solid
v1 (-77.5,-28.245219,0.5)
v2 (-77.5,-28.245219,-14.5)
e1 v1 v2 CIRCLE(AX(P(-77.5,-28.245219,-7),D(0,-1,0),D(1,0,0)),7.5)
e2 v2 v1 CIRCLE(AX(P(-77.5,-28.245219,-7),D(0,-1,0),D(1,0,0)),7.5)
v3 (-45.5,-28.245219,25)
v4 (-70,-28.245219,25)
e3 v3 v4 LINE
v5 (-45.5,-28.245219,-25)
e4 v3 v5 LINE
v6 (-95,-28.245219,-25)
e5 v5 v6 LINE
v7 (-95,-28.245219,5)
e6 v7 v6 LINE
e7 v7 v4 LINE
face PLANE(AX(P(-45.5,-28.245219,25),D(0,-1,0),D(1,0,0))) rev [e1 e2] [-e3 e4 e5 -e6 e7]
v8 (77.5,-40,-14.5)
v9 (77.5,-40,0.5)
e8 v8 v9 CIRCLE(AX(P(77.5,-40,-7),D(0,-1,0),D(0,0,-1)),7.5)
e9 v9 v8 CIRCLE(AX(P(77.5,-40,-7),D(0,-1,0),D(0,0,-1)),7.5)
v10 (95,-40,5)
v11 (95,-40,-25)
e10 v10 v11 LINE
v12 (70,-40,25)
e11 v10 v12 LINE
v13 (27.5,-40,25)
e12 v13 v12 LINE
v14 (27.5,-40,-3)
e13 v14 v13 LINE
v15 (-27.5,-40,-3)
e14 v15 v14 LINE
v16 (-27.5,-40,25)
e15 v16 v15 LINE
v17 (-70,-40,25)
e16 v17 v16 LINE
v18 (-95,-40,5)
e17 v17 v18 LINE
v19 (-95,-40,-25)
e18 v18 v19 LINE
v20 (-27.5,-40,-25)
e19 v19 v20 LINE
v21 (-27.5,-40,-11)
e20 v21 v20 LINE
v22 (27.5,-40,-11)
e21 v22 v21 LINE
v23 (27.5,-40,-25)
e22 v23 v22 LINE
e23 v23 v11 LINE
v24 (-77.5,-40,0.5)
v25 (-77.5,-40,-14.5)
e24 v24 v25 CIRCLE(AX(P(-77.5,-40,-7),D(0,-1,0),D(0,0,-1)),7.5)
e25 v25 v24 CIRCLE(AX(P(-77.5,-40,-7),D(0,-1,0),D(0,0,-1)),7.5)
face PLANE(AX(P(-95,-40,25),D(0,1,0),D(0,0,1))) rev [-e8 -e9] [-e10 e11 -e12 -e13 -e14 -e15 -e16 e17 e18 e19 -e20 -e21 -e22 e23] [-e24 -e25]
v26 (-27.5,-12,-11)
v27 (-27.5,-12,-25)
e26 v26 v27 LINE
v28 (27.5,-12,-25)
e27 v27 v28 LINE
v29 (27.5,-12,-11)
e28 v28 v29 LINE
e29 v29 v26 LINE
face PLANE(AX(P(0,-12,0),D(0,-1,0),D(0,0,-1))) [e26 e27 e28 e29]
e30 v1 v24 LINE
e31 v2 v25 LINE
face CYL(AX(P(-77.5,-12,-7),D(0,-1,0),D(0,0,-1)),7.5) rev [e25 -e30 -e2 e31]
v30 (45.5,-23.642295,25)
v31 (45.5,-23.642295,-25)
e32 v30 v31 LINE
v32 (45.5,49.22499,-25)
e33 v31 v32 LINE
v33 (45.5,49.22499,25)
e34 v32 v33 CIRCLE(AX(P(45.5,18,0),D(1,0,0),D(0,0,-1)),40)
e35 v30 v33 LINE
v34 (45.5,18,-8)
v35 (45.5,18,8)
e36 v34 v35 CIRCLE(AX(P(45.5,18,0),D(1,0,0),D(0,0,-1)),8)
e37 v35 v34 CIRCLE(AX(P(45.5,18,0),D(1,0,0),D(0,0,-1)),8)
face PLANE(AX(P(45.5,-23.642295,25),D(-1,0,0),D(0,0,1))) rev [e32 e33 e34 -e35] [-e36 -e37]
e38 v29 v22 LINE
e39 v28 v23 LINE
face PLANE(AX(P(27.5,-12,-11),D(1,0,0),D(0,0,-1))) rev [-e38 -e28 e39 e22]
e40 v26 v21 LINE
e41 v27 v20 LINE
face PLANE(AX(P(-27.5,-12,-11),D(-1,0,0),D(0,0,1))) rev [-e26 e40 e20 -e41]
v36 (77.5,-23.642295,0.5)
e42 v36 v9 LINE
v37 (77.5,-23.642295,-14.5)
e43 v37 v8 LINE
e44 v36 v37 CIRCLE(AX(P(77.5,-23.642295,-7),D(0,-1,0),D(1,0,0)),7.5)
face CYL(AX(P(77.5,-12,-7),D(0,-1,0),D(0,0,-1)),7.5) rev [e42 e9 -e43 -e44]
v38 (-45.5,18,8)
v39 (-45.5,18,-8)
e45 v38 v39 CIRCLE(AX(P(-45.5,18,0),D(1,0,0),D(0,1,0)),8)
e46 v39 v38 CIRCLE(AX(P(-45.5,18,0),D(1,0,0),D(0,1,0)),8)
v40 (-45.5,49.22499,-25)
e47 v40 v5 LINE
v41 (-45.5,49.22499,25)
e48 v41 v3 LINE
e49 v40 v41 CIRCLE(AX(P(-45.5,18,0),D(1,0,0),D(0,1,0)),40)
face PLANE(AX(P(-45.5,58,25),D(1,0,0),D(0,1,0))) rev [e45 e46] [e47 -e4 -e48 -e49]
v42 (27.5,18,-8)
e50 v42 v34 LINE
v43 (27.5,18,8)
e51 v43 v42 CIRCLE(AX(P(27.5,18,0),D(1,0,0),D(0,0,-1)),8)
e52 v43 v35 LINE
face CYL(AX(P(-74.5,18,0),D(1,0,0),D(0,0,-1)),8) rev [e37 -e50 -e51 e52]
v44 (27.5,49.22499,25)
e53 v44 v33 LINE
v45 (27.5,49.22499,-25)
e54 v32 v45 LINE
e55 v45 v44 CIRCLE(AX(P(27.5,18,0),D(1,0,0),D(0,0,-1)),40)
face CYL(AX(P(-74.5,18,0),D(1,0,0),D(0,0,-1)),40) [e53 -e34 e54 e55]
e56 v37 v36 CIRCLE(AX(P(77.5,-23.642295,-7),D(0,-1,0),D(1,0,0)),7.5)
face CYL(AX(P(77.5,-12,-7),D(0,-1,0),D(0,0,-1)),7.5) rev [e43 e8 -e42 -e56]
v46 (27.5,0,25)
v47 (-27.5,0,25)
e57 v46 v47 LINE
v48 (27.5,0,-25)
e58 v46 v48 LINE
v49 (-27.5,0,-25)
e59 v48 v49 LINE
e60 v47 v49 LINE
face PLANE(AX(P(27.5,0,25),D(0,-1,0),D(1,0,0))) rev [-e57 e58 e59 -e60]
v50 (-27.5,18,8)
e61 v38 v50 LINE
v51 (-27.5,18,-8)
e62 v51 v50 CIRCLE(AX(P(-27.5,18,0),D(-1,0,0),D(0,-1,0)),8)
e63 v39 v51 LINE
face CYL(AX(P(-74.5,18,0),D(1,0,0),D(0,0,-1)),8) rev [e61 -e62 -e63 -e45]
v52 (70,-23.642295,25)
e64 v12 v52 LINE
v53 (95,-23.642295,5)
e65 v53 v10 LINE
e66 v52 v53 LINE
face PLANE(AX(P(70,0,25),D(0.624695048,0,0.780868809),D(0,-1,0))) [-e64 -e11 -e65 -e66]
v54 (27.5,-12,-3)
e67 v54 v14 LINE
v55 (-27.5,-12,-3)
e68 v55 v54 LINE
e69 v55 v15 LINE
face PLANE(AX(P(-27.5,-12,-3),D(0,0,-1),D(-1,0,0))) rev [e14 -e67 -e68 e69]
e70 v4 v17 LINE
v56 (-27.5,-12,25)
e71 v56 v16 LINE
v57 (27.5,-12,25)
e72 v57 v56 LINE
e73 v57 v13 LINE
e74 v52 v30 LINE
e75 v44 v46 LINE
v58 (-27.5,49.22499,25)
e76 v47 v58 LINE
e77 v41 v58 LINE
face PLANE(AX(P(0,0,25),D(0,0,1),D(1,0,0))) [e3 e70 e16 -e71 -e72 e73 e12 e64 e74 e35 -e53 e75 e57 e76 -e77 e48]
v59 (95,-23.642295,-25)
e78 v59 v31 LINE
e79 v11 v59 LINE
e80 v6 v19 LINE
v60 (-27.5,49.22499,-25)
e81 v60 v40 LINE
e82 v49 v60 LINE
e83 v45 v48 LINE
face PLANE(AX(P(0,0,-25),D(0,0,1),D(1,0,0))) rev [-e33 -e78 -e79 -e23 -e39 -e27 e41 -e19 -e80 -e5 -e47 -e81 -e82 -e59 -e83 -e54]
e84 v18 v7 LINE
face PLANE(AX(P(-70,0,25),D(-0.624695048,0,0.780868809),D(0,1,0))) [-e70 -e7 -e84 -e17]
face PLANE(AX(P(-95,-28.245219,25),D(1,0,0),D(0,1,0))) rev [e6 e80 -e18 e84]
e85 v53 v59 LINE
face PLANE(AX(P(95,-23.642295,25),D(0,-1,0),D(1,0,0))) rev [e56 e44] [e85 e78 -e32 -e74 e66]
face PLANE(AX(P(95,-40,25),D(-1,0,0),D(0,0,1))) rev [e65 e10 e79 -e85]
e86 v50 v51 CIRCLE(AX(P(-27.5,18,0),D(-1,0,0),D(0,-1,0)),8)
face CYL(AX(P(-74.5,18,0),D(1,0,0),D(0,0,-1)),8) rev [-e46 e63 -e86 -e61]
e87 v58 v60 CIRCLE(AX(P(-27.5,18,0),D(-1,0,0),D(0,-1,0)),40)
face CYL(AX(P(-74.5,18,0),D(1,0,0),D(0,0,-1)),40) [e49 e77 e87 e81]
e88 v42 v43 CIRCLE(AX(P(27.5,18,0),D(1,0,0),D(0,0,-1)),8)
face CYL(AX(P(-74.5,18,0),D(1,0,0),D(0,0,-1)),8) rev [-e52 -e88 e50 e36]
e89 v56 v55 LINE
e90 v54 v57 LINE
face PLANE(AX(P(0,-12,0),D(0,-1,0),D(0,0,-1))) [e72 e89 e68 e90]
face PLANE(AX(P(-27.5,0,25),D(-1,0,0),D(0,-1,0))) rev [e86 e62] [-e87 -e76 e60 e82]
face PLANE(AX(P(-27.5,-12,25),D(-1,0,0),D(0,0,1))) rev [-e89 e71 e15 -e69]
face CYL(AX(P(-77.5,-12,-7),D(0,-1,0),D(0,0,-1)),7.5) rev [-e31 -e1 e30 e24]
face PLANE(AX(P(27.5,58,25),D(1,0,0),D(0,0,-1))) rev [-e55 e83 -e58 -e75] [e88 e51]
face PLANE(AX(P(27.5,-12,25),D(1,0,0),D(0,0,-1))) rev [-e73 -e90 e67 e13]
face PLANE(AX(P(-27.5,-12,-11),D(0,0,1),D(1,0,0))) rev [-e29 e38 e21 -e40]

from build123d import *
from OCP.BRepFilletAPI import BRepFilletAPI_MakeChamfer

# Parameters (mm, degrees)
BRACKET_BODY_DEPTH                           = 25
UPRIGHT_ROUNDS_AND_PIN_HOLE_SKETCH_R         = 8
UPRIGHT_ROUNDS_AND_PIN_HOLE_16_DEPTH         = 120
FLANGE_CORNER_CHAMFERS_SIZE                  = 20
FLANGE_CORNER_CHAMFERS_SIZE2                 = 25
MOUNTING_HOLES_AND_RELIEF_SKETCH_R           = 7.5
MOUNTING_HOLES_AND_RELIEF_SKETCH_W           = 55
MOUNTING_HOLES_AND_RELIEF_SKETCH_H           = 28
MOUNTING_HOLES_AND_RELIEF_SKETCH_H_2         = 14
MOUNTING_HOLES_2X_15_AND_CENTRE_RELIEF_DEPTH = 28


with BuildPart() as part:
    # Bracket Side Profile Sketch → Bracket Body (new, symmetric)
    with BuildSketch(Plane.XY):
        Polygon((-95, -28.245219348), (-95, -40), (95, -40), (95, -23.642294713), (45.5, -23.642294713), (45.5, 58), (27.5, 58), (27.5, 0), (-27.5, 0), (-27.5, 58), (-45.5, 58), (-45.5, -28.245219348), align=None)
    extrude(amount=BRACKET_BODY_DEPTH, both=True)

    # Upright Rounds and Pin Hole Sketch → Upright Rounds and Pin Hole Ø16 (cut)
    with BuildSketch(Plane(origin=(45.5, 0, 0), x_dir=(0, 0, -1), z_dir=(1, 0, 0))):
        with BuildLine():
            Line((-25, 58), (-25, 49.224989992))
            ThreePointArc((-25, 49.224989992), (-13.24764886, 55.74254628), (-1.3e-08, 58))
            Line((-1.3e-08, 58), (-25, 58))
        make_face()
        Polygon((-25, 66.800794381), (-25, 58), (-1.3e-08, 58), (25, 58), (25, 66.800794381), align=None)
        with BuildLine():
            Line((25, 58), (-1.3e-08, 58))
            ThreePointArc((-1.3e-08, 58), (13.247648848, 55.742546284), (25, 49.224989992))
            Line((25, 49.224989992), (25, 58))
        make_face()
        with Locations((0, 18)):
            Circle(UPRIGHT_ROUNDS_AND_PIN_HOLE_SKETCH_R)
    extrude(amount=-UPRIGHT_ROUNDS_AND_PIN_HOLE_16_DEPTH, mode=Mode.SUBTRACT)

    # Flange Corner Chamfers: one chamfer whose edges measure the first distance from different faces: ONE call of the kernel's chamfer builder (chamfer() names one face for all edges)
    flange_corner_chamfers_edges_1 = [part.edges().sort_by_distance(p)[0] for p in [
        (95, -31.821147357, 25),
    ]]
    flange_corner_chamfers_side_1 = [part.faces().sort_by_distance(p)[0] for p in [
        (95, -31.821147357, 0),
    ]]
    flange_corner_chamfers_edges_2 = [part.edges().sort_by_distance(p)[0] for p in [
        (-95, -34.122609674, 25),
    ]]
    flange_corner_chamfers_side_2 = [part.faces().sort_by_distance(p)[0] for p in [
        (-95, -34.122609674, 0),
    ]]
    flange_corner_chamfers = BRepFilletAPI_MakeChamfer(part.part.solid().wrapped)
    for e in flange_corner_chamfers_edges_1:
        flange_corner_chamfers.Add(FLANGE_CORNER_CHAMFERS_SIZE, FLANGE_CORNER_CHAMFERS_SIZE2, e.wrapped, flange_corner_chamfers_side_1[0].wrapped)  # the first distance lies on this face
    for e in flange_corner_chamfers_edges_2:
        flange_corner_chamfers.Add(FLANGE_CORNER_CHAMFERS_SIZE, FLANGE_CORNER_CHAMFERS_SIZE2, e.wrapped, flange_corner_chamfers_side_2[0].wrapped)  # the first distance lies on this face
    add(Compound.cast(flange_corner_chamfers.Shape()), mode=Mode.REPLACE)

    # Mounting Holes and Relief Sketch → Mounting Holes 2xØ15 and Centre Relief (cut)
    with BuildSketch(Plane.XZ.offset(40)):
        with Locations(Location((-77.5, -7, 0), (0, 0, 270))):
            Circle(MOUNTING_HOLES_AND_RELIEF_SKETCH_R)
        with Locations(Location((77.5, -7, 0), (0, 0, 270))):
            Circle(MOUNTING_HOLES_AND_RELIEF_SKETCH_R)
        with Locations((0, 11)):
            Rectangle(MOUNTING_HOLES_AND_RELIEF_SKETCH_W, MOUNTING_HOLES_AND_RELIEF_SKETCH_H)
        with Locations((0, -18)):
            Rectangle(MOUNTING_HOLES_AND_RELIEF_SKETCH_W, MOUNTING_HOLES_AND_RELIEF_SKETCH_H_2)
    extrude(amount=-MOUNTING_HOLES_2X_15_AND_CENTRE_RELIEF_DEPTH, mode=Mode.SUBTRACT)


solid = part.part
